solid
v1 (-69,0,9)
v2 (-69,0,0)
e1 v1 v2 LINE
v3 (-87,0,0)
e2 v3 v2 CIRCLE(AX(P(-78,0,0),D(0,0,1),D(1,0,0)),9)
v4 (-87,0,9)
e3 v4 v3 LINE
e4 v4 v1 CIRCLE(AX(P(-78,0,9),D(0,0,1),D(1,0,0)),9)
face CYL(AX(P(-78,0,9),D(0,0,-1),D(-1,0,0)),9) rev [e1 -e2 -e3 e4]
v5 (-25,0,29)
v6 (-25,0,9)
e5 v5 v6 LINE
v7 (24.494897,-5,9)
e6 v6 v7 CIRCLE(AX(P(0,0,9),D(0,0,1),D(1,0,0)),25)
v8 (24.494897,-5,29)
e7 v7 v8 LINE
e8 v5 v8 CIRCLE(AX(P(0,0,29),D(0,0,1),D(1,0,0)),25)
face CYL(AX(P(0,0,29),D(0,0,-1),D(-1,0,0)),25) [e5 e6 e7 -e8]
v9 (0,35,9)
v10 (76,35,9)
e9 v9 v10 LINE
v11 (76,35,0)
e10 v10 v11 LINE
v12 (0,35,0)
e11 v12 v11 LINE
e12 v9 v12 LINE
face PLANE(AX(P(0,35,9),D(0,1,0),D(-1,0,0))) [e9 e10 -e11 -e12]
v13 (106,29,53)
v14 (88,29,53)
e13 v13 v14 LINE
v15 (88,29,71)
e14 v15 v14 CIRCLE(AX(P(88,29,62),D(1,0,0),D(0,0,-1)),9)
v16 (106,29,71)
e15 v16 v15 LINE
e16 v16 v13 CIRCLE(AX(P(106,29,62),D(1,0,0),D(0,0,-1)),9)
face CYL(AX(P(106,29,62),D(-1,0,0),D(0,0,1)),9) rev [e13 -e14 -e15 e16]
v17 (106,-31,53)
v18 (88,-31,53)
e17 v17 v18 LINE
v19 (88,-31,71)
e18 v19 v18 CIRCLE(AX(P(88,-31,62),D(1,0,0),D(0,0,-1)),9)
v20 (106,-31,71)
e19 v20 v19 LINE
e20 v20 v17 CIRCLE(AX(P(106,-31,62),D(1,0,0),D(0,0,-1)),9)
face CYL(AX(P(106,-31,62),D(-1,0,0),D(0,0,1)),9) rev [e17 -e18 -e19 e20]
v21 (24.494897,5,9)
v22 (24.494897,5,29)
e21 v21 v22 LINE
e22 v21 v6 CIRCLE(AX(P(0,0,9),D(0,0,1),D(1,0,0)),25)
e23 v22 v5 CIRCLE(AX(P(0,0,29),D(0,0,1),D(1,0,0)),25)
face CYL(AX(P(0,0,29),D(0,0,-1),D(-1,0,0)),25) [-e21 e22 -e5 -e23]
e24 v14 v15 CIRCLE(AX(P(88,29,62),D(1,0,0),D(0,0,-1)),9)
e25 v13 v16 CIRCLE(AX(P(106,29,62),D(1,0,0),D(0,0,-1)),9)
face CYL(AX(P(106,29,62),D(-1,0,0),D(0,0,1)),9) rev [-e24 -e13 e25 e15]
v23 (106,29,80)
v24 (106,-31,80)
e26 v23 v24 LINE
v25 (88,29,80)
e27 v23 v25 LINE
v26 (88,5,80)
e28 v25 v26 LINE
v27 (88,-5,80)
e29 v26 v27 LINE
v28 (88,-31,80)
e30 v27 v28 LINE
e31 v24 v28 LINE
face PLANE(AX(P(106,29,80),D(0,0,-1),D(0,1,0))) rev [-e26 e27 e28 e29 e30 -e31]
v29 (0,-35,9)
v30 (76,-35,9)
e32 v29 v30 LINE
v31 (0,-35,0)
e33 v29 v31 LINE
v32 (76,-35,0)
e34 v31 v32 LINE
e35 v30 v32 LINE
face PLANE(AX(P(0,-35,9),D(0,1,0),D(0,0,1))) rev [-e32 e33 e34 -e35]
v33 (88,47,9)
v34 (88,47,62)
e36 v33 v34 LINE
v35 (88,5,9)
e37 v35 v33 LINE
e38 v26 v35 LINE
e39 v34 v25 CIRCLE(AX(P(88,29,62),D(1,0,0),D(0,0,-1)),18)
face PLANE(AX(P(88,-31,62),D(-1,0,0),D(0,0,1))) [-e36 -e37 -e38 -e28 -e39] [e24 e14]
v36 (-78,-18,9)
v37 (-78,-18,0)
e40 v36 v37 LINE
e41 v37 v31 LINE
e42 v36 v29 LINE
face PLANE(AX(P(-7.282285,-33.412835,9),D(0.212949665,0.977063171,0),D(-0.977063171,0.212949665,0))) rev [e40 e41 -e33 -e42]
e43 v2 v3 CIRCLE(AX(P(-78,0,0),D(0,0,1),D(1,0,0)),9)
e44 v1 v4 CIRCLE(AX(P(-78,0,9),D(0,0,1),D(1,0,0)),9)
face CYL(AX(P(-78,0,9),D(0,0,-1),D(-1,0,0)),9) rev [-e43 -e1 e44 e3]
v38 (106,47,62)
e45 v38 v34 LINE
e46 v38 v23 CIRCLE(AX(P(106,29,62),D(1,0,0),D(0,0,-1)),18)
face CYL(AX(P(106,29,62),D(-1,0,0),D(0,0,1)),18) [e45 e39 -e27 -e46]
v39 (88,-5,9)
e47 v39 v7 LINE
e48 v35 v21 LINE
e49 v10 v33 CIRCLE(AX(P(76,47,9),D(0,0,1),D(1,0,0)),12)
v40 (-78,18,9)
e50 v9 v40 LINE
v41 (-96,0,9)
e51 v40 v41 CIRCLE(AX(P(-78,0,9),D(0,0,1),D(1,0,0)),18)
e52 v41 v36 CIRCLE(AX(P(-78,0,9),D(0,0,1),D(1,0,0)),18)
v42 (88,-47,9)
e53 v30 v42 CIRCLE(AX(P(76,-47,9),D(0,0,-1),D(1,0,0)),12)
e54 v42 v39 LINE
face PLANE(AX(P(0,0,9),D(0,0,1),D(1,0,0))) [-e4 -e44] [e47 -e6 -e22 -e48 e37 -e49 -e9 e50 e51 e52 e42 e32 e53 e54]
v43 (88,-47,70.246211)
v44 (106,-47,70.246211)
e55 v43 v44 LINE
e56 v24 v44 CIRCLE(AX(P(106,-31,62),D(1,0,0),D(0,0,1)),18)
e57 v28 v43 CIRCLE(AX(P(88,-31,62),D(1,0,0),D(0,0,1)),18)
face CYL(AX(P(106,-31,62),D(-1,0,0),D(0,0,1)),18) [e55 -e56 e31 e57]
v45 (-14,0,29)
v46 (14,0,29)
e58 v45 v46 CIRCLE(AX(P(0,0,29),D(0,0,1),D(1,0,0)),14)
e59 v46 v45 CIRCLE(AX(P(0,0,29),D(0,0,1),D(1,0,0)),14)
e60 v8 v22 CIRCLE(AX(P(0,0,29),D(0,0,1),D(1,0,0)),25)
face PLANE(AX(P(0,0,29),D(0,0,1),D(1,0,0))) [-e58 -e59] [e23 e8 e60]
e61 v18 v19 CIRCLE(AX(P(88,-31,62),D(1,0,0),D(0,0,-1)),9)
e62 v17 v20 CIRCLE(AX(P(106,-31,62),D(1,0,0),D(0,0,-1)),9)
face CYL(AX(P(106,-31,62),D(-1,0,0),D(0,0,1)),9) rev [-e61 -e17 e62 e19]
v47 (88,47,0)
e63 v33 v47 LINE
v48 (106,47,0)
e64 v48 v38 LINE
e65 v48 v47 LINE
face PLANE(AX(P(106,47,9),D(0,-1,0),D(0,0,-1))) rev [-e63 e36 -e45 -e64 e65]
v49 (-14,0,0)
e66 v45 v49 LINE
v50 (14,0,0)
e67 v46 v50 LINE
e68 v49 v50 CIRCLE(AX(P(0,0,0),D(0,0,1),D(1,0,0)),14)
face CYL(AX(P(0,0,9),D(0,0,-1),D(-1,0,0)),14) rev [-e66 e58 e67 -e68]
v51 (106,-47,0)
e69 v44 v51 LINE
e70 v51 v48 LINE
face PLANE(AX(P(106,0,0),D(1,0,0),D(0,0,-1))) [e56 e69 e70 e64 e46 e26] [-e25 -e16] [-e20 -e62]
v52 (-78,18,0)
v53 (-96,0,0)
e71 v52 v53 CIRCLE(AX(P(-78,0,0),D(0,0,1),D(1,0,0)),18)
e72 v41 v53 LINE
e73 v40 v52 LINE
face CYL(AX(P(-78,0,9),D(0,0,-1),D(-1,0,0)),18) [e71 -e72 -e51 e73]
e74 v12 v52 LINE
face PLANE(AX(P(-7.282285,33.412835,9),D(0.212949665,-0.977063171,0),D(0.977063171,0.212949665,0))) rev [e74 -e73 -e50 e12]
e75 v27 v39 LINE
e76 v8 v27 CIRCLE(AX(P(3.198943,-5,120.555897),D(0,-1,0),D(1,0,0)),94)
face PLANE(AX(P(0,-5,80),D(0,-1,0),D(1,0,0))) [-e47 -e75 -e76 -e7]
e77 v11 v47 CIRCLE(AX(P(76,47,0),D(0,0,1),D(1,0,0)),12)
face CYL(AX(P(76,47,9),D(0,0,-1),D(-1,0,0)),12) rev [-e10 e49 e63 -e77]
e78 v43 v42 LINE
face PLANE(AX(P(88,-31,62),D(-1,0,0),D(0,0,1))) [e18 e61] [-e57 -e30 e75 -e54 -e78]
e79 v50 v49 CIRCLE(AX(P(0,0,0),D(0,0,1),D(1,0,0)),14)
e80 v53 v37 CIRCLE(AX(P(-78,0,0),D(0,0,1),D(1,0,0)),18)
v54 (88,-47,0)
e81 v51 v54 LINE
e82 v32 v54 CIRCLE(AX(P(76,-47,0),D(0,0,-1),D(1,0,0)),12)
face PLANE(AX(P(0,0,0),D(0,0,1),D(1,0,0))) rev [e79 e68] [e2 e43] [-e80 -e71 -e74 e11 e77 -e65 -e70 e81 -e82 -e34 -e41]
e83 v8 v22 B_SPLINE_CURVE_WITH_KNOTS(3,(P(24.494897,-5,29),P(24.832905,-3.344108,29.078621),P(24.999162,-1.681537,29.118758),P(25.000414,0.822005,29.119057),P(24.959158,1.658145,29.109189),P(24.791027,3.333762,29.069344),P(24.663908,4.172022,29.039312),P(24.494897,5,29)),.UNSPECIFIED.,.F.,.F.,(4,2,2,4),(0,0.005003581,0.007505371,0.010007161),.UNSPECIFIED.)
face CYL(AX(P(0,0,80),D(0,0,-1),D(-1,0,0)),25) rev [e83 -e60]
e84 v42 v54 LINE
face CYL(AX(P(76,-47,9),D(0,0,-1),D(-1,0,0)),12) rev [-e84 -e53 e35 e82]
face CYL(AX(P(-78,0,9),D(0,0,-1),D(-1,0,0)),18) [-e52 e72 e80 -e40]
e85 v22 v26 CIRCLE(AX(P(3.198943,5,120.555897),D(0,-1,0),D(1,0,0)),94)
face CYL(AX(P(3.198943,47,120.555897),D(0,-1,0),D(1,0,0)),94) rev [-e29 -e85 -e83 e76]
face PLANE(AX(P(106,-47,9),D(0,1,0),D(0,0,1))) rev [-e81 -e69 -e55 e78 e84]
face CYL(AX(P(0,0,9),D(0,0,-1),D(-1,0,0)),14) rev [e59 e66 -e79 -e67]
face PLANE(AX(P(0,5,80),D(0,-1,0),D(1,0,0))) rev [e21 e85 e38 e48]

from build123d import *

# Parameters (mm, degrees)
ARM_PLATE_SKETCH_R        = 9
ARM_PLATE_SKETCH_R_2      = 14
ARM_PLATE_DEPTH           = 9
MOUNTING_FLANGE_SKETCH_R  = 9
MOUNTING_FLANGE_DEPTH     = 18
CONNECTING_BLOCK_SKETCH_W = 9
CONNECTING_BLOCK_SKETCH_H = 94
CONNECTING_BLOCK_DEPTH    = 18
HUB_BOSS_SKETCH_R         = 25
HUB_BOSS_SKETCH_R_2       = 14
HUB_BOSS_DEPTH            = 20
SUPPORT_RIB_DEPTH         = 71
PROFILE_TRIM_CUT_DEPTH    = 143.618371888
FLANGE_CUT_SKETCH_W       = 18
FLANGE_CUT_SKETCH_H       = 2
FLANGE_CUT_DEPTH          = 137.667479724


with BuildPart() as part:
    # Arm Plate Sketch → Arm Plate (new body)
    with BuildSketch(Plane.XY):
        with BuildLine():
            Line((76, 35), (0, 35))
            Line((0, 35), (-78, 18))
            ThreePointArc((-78, 18), (-96, 0), (-78, -18))
            Line((-78, -18), (0, -35))
            Line((0, -35), (76, -35))
            ThreePointArc((76, -35), (84.485281374, -38.514718626), (88, -47))
            Line((88, -47), (88, 47))
            ThreePointArc((88, 47), (84.485281374, 38.514718626), (76, 35))
        make_face()
        with Locations((-78, 0)):
            Circle(ARM_PLATE_SKETCH_R, mode=Mode.SUBTRACT)
        Circle(ARM_PLATE_SKETCH_R_2, mode=Mode.SUBTRACT)
    extrude(amount=ARM_PLATE_DEPTH)



with BuildPart() as body_2:
    # Mounting Flange Sketch → Mounting Flange (new body)
    with BuildSketch(Plane(origin=(88, 0, 0), x_dir=(0, 0, -1), z_dir=(1, 0, 0))):
        with BuildLine():
            Line((-9, 47), (-62, 47))
            ThreePointArc((-62, 47), (-74.727922061, 41.727922061), (-80, 29))
            Line((-80, 29), (-80, -31))
            ThreePointArc((-80, -31), (-74.727922061, -43.727922061), (-62, -49))
            Line((-62, -49), (-9, -49))
            Line((-9, -49), (-9, 47))
        make_face()
        with Locations((-62, 29)):
            Circle(MOUNTING_FLANGE_SKETCH_R, mode=Mode.SUBTRACT)
        with Locations((-62, -31)):
            Circle(MOUNTING_FLANGE_SKETCH_R, mode=Mode.SUBTRACT)
    extrude(amount=MOUNTING_FLANGE_DEPTH)


with BuildPart() as part_1:
    add(part.part)

    add(body_2.part)  # Connecting Block merges body 2
    # Connecting Block Sketch → Connecting Block (add)
    with BuildSketch(Plane(origin=(88, 0, 0), x_dir=(0, 0, -1), z_dir=(1, 0, 0))):
        with Locations((-4.5, 0)):
            Rectangle(CONNECTING_BLOCK_SKETCH_W, CONNECTING_BLOCK_SKETCH_H)
    extrude(amount=CONNECTING_BLOCK_DEPTH)

    # Hub Boss Sketch → Hub Boss (add)
    with BuildSketch(Plane.XY.offset(9)):
        Circle(HUB_BOSS_SKETCH_R)
        Circle(HUB_BOSS_SKETCH_R_2, mode=Mode.SUBTRACT)
    extrude(amount=HUB_BOSS_DEPTH)

    # Support Rib Sketch → Support Rib (add)
    with BuildSketch(Plane.XY.offset(9)):
        with BuildLine():
            Line((88, 0), (88, 5))
            Line((88, 5), (24.494897428, 5))
            ThreePointArc((24.494897428, 5), (24.873403825, 2.51272405), (25, 0))
            ThreePointArc((25, 0), (24.873403825, -2.51272405), (24.494897428, -5))
            Line((24.494897428, -5), (88, -5))
            Line((88, -5), (88, 0))
        make_face()
    extrude(amount=SUPPORT_RIB_DEPTH)

    # Profile Trim Cut Sketch → Profile Trim Cut (cut, through all)
    with BuildSketch(Plane.XZ.offset(5)):
        with BuildLine():
            Line((88, 80), (24.494897428, 80))
            Line((24.494897428, 80), (24.494897428, 29))
            ThreePointArc((24.494897428, 29), (62.058045644, 47.264655803), (88, 80))
        make_face()
    extrude(amount=-PROFILE_TRIM_CUT_DEPTH, mode=Mode.SUBTRACT)

    # Flange Cut Sketch → Flange Cut (cut, through all)
    with BuildSketch(Plane(origin=(0, 0, 9), x_dir=(-1, 0, 0), z_dir=(0, 0, -1))):
        with Locations((-97, -48)):
            Rectangle(FLANGE_CUT_SKETCH_W, FLANGE_CUT_SKETCH_H)
    extrude(amount=-FLANGE_CUT_DEPTH, mode=Mode.SUBTRACT)


solid = part_1.part
